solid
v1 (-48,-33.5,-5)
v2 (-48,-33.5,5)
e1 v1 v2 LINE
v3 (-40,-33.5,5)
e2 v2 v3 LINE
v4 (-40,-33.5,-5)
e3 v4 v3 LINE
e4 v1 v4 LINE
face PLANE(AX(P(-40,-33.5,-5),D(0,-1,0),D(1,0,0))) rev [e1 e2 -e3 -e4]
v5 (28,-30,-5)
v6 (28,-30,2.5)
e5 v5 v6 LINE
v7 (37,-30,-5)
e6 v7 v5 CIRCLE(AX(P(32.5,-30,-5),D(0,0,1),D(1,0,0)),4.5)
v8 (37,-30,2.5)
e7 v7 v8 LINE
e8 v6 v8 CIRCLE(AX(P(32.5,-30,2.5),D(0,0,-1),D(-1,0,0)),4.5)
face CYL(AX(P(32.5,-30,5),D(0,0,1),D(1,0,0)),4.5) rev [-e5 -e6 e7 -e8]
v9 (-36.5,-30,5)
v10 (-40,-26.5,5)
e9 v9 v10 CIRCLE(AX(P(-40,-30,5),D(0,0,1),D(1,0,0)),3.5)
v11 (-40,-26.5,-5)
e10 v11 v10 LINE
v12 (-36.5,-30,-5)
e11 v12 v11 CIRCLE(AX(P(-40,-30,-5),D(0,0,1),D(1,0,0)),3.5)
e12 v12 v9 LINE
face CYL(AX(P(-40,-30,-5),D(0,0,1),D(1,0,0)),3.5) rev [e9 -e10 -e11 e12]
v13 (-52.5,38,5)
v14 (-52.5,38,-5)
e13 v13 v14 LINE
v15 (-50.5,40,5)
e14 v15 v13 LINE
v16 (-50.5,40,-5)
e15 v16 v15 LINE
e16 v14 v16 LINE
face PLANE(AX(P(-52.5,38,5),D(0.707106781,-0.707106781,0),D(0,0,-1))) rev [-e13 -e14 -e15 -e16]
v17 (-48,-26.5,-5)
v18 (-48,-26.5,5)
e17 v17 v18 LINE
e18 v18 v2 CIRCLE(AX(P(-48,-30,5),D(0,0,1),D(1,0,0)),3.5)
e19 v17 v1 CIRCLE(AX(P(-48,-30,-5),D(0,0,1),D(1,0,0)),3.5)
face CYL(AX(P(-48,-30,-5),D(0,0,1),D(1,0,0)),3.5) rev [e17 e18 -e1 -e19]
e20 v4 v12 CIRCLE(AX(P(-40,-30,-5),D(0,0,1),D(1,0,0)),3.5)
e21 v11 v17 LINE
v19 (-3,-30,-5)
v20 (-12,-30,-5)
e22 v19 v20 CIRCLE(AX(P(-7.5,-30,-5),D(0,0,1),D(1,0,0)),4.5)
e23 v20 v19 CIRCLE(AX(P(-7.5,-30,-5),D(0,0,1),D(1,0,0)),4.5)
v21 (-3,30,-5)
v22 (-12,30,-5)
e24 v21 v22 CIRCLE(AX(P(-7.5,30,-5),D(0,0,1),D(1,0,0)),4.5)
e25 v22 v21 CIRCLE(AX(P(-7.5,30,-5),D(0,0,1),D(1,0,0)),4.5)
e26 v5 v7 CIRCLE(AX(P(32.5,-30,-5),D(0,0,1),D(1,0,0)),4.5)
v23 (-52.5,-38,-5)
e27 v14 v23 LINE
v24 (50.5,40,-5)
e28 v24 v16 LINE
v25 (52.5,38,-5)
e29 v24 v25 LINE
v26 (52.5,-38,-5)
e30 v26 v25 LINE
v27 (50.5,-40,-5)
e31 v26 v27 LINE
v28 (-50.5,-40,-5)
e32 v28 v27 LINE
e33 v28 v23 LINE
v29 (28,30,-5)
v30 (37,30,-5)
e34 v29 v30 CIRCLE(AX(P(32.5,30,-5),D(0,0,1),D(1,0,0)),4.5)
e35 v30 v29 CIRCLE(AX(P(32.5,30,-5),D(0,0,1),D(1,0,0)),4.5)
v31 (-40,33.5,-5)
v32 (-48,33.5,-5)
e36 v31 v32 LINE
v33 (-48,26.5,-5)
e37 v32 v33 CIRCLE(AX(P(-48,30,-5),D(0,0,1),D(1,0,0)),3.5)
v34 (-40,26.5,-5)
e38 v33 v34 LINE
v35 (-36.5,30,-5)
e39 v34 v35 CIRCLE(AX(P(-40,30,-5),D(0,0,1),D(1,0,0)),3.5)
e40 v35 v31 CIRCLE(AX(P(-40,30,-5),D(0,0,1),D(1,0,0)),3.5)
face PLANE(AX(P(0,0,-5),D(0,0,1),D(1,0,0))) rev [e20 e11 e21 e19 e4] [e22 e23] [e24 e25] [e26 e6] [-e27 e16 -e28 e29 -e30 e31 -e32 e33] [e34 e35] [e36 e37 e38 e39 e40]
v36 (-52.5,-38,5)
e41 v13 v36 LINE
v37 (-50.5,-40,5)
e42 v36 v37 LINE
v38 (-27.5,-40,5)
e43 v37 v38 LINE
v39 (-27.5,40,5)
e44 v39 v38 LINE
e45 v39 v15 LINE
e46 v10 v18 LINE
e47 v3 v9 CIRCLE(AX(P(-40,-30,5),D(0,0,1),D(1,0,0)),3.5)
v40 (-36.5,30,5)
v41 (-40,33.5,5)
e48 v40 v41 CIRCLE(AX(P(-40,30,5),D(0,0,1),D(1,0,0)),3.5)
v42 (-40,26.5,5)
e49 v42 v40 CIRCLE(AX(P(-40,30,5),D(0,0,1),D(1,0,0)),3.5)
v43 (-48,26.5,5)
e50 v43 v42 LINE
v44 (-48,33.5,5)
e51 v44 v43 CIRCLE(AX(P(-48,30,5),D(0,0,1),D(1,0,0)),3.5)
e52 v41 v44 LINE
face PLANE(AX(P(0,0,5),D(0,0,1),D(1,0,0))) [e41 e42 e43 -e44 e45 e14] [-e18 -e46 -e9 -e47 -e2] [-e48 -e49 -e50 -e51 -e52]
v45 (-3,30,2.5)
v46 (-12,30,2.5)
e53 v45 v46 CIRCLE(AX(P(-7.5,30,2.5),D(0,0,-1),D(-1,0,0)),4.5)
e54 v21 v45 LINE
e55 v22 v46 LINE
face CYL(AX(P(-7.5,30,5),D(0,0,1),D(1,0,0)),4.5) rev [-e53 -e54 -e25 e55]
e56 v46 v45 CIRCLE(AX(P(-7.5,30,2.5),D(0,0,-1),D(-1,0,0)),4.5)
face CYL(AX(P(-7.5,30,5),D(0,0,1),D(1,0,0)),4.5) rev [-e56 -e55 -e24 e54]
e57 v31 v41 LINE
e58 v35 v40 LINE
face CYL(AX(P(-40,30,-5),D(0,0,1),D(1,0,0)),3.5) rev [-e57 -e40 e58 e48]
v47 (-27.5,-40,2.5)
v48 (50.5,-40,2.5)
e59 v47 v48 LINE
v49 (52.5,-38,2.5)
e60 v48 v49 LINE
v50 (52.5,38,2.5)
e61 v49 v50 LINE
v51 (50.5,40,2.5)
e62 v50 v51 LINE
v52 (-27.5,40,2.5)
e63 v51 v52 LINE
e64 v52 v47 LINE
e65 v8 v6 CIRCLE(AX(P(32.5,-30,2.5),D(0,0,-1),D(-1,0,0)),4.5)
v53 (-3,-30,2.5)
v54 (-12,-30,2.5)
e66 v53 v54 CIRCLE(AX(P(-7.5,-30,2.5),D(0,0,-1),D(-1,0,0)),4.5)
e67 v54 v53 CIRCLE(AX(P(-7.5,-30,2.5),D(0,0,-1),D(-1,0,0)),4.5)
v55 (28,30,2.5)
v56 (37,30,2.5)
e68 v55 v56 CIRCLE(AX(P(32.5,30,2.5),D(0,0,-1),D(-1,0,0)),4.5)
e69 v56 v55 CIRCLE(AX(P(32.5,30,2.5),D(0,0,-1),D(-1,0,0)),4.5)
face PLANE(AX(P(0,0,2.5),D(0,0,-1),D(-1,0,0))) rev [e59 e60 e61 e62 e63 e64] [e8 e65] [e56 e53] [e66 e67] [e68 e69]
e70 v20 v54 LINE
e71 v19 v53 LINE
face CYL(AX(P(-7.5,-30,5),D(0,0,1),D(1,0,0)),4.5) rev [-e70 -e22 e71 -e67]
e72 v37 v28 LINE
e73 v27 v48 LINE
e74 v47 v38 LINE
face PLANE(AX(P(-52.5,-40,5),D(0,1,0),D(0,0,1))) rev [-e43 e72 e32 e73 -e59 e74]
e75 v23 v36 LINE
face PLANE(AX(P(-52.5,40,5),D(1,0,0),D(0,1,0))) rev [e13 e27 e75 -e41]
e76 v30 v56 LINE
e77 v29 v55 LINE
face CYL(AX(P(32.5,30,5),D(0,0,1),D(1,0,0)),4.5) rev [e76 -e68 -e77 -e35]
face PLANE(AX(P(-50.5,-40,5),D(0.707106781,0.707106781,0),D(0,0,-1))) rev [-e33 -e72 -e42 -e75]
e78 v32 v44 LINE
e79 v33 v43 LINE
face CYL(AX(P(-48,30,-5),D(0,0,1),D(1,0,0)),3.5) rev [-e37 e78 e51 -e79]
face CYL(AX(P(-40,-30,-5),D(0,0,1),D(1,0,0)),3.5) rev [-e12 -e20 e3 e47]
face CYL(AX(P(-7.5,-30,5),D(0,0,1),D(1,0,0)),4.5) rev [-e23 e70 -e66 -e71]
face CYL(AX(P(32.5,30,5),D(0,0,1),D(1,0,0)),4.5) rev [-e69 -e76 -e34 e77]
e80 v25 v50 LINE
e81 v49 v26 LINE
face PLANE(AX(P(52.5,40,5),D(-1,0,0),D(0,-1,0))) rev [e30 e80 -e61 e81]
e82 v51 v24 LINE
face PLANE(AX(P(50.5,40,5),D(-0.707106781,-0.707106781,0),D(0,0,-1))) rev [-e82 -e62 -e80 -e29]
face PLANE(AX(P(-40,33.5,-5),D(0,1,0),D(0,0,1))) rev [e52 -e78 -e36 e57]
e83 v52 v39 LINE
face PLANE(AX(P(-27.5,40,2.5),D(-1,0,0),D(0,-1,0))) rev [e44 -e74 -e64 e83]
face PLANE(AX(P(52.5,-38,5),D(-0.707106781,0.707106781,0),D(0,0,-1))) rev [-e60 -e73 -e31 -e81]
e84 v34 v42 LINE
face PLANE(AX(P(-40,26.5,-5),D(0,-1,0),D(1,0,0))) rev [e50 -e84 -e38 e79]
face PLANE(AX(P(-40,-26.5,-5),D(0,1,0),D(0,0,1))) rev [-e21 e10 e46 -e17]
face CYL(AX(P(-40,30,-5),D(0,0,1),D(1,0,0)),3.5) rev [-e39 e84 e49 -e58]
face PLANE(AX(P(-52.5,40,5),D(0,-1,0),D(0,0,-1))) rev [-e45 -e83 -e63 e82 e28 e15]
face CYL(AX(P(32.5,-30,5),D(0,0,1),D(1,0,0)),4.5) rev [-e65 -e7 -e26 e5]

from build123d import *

# Parameters (mm, degrees)
SKETCH_1_W             = 105
SKETCH_1_H             = 80
EXTRUDE_1_DEPTH        = 5
SKETCH_2_W             = 80
SKETCH_2_H             = 80
CUT_EXTRUDE_1_DEPTH    = 2.5
HOLE_WIZARD_9_0_9_1_D  = 9
HOLE_WIZARD_7_0_7_1_D  = 7
CHAMFER_1_SIZE         = 2
CUT_EXTRUDE_3_DEPTH    = 10
PATTERN_LINEAR_1_COUNT = 2
PATTERN_LINEAR_1_PITCH = 60


with BuildPart() as part:
    # 草图1 → 凸台-拉伸1 (new, symmetric)
    with BuildSketch(Plane.XY):
        Rectangle(SKETCH_1_W, SKETCH_1_H)
    extrude(amount=EXTRUDE_1_DEPTH, both=True)

    # 草图2 → 切除-拉伸1 (cut)
    with BuildSketch(Plane.XY.offset(5)):
        with Locations((12.5, 0)):
            Rectangle(SKETCH_2_W, SKETCH_2_H)
    extrude(amount=-CUT_EXTRUDE_1_DEPTH, mode=Mode.SUBTRACT)

    # Ø9.0 (9) 直径孔1 (through all)
    with Locations(Plane.XY.offset(5)):
        with Locations((-7.5, 30), (32.5, 30), (32.5, -30), (-7.5, -30)):
            Hole(HOLE_WIZARD_9_0_9_1_D / 2)

    # Ø7.0 (7) 直径孔1 (through all)
    with Locations(Plane.XY.offset(5)):
        with Locations((-44, 30), (-86, 30), (-44, -30), (-86, -30)):
            Hole(HOLE_WIZARD_7_0_7_1_D / 2)

    # 倒角1
    chamfer_1_edges = [part.edges().sort_by_distance(p)[0] for p in [
        (52.5, -40, -1.25),
        (52.5, 40, -1.25),
        (-52.5, -40, 0),
        (-52.5, 40, 0),
    ]]
    chamfer(chamfer_1_edges, length=CHAMFER_1_SIZE)

    # 草图8 → 切除-拉伸3 (cut)
    with BuildSketch(Plane.XY.offset(5)):
        with BuildLine():
            Line((-40, 26.5), (-48, 26.5))
            ThreePointArc((-48, 26.5), (-51.5, 30), (-48, 33.5))
            Line((-48, 33.5), (-40, 33.5))
            ThreePointArc((-40, 33.5), (-36.5, 30), (-40, 26.5))
        make_face()
    cut_extrude_3 = extrude(amount=-CUT_EXTRUDE_3_DEPTH, mode=Mode.SUBTRACT)

    # 阵列(线性)1: 切除-拉伸3 ×2
    with Locations(*[(0, -i * PATTERN_LINEAR_1_PITCH, 0) for i in range(1, PATTERN_LINEAR_1_COUNT)]):
        add(cut_extrude_3, mode=Mode.SUBTRACT)


solid = part.part
